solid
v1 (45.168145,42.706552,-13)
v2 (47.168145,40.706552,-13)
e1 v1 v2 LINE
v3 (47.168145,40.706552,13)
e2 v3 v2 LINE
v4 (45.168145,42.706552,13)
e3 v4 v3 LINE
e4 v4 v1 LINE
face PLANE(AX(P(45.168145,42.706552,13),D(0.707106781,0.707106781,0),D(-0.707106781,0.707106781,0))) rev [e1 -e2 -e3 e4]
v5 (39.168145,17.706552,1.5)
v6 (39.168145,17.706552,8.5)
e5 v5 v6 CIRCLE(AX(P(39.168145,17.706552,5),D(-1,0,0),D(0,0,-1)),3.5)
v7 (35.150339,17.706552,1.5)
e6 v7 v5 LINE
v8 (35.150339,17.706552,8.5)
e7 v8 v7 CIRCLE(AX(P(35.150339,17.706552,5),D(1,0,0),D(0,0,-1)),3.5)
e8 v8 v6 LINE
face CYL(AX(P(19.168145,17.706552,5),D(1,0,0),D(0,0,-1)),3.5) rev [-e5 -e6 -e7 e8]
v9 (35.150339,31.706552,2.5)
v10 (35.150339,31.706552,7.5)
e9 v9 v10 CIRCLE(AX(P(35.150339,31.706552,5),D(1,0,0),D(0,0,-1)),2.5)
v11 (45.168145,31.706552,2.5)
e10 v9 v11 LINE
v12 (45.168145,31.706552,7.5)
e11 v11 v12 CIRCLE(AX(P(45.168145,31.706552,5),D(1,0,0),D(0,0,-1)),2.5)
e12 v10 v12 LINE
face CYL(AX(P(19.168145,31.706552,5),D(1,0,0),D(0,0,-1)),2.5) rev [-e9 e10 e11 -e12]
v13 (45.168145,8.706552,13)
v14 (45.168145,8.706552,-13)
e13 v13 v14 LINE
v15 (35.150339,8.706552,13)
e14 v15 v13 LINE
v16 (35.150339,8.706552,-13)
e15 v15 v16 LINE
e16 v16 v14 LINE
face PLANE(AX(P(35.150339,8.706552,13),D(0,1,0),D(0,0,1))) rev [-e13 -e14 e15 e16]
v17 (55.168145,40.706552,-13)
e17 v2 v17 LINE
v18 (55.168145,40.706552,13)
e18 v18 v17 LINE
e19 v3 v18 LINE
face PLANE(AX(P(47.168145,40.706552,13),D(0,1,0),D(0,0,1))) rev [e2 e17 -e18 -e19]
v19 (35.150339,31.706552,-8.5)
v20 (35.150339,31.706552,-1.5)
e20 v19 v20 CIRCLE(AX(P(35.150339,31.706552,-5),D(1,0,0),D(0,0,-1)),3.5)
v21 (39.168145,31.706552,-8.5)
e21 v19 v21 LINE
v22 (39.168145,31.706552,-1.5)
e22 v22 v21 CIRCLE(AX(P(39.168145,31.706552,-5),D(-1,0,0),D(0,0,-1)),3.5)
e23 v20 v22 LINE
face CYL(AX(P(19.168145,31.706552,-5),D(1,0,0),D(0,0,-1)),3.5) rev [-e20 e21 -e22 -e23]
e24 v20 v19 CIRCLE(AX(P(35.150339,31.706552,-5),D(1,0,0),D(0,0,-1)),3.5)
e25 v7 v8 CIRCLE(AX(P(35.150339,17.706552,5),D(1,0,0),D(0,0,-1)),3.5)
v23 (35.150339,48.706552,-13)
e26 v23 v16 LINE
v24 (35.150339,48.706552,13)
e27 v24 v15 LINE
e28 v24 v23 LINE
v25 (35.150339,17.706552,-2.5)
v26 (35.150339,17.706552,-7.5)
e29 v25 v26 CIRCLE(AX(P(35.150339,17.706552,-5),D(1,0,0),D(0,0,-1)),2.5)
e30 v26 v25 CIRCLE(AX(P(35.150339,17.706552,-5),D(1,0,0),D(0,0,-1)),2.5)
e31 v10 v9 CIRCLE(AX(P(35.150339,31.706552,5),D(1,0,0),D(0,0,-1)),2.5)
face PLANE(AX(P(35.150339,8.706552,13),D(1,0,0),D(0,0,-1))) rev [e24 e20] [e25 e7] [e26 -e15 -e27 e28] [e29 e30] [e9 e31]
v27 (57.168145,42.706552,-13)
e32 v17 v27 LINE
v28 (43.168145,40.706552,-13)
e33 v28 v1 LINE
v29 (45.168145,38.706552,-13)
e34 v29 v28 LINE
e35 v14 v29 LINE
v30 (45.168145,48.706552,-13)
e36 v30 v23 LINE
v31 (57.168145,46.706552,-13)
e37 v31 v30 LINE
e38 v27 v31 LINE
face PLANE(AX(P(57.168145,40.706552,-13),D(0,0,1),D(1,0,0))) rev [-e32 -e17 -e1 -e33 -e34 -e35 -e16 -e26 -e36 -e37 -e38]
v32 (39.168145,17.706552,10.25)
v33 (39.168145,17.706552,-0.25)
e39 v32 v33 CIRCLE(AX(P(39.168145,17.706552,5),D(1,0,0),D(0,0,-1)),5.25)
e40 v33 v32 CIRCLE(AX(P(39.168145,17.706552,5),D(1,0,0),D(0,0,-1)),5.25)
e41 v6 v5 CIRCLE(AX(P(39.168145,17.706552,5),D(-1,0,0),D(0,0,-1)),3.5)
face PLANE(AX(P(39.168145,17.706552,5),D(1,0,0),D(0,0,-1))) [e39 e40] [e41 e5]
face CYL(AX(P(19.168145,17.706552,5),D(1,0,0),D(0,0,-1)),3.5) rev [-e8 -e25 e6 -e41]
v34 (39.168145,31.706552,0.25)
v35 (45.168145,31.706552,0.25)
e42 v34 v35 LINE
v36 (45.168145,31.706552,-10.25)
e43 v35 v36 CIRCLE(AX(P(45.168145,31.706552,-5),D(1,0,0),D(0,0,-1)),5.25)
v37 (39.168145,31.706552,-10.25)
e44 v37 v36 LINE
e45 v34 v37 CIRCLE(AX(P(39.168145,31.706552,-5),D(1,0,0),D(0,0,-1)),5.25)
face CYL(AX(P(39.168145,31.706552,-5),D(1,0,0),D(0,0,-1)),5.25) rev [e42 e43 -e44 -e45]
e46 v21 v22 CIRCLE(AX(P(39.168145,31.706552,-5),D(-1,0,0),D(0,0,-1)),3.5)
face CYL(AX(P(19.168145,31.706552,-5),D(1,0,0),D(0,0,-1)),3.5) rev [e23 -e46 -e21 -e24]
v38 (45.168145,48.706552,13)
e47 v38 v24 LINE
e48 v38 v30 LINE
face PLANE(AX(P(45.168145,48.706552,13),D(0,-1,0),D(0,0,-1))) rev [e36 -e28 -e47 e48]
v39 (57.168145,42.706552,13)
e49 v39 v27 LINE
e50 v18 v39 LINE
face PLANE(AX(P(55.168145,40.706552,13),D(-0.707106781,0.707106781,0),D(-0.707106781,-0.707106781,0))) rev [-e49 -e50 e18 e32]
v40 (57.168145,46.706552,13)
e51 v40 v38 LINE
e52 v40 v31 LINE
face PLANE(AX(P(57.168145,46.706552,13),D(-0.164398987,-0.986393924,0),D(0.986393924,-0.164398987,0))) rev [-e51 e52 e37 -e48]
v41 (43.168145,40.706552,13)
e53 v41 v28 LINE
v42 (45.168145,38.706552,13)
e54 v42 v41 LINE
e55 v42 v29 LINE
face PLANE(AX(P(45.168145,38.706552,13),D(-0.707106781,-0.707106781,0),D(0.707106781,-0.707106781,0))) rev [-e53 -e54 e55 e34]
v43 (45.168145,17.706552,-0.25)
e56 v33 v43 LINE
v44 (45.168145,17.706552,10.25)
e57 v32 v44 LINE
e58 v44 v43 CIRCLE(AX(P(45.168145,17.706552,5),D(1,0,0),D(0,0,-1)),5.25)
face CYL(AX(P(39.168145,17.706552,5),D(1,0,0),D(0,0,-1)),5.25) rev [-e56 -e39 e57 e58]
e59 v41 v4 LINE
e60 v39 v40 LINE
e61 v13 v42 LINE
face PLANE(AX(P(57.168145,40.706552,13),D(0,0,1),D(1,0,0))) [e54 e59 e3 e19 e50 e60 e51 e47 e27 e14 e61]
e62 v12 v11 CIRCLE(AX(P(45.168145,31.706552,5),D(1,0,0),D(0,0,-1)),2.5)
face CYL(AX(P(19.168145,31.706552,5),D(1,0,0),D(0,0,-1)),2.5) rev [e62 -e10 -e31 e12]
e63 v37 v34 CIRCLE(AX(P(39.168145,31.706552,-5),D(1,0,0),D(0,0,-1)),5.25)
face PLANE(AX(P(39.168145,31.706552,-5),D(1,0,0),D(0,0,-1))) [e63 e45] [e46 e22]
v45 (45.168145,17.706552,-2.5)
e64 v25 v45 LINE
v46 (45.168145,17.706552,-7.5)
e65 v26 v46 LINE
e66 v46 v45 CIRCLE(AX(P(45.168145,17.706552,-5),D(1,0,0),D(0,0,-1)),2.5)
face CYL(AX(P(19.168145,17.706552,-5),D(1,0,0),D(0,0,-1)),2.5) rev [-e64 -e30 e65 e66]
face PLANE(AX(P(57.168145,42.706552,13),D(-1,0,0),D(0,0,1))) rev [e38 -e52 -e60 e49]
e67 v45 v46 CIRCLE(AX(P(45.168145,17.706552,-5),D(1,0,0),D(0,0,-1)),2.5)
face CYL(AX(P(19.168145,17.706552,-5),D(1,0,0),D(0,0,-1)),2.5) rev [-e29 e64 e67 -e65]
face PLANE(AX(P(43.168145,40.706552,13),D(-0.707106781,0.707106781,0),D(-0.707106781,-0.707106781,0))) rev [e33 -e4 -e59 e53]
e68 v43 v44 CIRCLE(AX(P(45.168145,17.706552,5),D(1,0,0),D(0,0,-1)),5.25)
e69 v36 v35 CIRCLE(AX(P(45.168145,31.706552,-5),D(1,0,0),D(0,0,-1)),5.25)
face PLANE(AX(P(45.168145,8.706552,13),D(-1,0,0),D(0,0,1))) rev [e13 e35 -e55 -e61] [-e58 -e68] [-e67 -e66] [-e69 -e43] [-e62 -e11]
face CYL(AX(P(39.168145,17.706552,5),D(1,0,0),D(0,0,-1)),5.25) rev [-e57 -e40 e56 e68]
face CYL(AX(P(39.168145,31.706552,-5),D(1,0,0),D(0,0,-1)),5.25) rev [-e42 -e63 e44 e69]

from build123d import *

# Parameters (mm, degrees)
BOSS_EXTRUDE1_DEPTH = 13
SKETCH2_R           = 3.5
SKETCH2_R_2         = 2.5
CUT_EXTRUDE1_DEPTH  = 26
SKETCH3_R           = 5.25
CUT_EXTRUDE2_DEPTH  = 6


with BuildPart() as part:
    # Sketch1 → Boss-Extrude1 (new, symmetric)
    with BuildSketch(Plane.XY):
        Polygon((55.168145317, 40.706551648), (57.168145317, 42.706551648), (57.168145317, 46.706551648), (45.168145317, 48.706551648), (35.15033873, 48.706551648), (35.15033873, 14.706551648), (35.15033873, 8.706551648), (45.168145317, 8.706551648), (45.168145317, 38.706551648), (43.168145317, 40.706551648), (45.168145317, 42.706551648), (47.168145317, 40.706551648), align=None)
    extrude(amount=BOSS_EXTRUDE1_DEPTH, both=True)

    # Sketch2 → Cut-Extrude1 (cut)
    with BuildSketch(Plane(origin=(45.168145317, 0, 0), x_dir=(0, 0, -1), z_dir=(1, 0, 0))):
        with Locations((-5, 17.706551648)):
            Circle(SKETCH2_R)
        with Locations((5, 31.706551648)):
            Circle(SKETCH2_R)
        with Locations((5, 17.706551648)):
            Circle(SKETCH2_R_2)
        with Locations((-5, 31.706551648)):
            Circle(SKETCH2_R_2)
    extrude(amount=-CUT_EXTRUDE1_DEPTH, mode=Mode.SUBTRACT)

    # Sketch3 → Cut-Extrude2 (cut)
    with BuildSketch(Plane(origin=(45.168145317, 0, 0), x_dir=(0, 0, -1), z_dir=(1, 0, 0))):
        with Locations((5, 31.706551648)):
            Circle(SKETCH3_R)
        with Locations((-5, 17.706551648)):
            Circle(SKETCH3_R)
    extrude(amount=-CUT_EXTRUDE2_DEPTH, mode=Mode.SUBTRACT)


solid = part.part
